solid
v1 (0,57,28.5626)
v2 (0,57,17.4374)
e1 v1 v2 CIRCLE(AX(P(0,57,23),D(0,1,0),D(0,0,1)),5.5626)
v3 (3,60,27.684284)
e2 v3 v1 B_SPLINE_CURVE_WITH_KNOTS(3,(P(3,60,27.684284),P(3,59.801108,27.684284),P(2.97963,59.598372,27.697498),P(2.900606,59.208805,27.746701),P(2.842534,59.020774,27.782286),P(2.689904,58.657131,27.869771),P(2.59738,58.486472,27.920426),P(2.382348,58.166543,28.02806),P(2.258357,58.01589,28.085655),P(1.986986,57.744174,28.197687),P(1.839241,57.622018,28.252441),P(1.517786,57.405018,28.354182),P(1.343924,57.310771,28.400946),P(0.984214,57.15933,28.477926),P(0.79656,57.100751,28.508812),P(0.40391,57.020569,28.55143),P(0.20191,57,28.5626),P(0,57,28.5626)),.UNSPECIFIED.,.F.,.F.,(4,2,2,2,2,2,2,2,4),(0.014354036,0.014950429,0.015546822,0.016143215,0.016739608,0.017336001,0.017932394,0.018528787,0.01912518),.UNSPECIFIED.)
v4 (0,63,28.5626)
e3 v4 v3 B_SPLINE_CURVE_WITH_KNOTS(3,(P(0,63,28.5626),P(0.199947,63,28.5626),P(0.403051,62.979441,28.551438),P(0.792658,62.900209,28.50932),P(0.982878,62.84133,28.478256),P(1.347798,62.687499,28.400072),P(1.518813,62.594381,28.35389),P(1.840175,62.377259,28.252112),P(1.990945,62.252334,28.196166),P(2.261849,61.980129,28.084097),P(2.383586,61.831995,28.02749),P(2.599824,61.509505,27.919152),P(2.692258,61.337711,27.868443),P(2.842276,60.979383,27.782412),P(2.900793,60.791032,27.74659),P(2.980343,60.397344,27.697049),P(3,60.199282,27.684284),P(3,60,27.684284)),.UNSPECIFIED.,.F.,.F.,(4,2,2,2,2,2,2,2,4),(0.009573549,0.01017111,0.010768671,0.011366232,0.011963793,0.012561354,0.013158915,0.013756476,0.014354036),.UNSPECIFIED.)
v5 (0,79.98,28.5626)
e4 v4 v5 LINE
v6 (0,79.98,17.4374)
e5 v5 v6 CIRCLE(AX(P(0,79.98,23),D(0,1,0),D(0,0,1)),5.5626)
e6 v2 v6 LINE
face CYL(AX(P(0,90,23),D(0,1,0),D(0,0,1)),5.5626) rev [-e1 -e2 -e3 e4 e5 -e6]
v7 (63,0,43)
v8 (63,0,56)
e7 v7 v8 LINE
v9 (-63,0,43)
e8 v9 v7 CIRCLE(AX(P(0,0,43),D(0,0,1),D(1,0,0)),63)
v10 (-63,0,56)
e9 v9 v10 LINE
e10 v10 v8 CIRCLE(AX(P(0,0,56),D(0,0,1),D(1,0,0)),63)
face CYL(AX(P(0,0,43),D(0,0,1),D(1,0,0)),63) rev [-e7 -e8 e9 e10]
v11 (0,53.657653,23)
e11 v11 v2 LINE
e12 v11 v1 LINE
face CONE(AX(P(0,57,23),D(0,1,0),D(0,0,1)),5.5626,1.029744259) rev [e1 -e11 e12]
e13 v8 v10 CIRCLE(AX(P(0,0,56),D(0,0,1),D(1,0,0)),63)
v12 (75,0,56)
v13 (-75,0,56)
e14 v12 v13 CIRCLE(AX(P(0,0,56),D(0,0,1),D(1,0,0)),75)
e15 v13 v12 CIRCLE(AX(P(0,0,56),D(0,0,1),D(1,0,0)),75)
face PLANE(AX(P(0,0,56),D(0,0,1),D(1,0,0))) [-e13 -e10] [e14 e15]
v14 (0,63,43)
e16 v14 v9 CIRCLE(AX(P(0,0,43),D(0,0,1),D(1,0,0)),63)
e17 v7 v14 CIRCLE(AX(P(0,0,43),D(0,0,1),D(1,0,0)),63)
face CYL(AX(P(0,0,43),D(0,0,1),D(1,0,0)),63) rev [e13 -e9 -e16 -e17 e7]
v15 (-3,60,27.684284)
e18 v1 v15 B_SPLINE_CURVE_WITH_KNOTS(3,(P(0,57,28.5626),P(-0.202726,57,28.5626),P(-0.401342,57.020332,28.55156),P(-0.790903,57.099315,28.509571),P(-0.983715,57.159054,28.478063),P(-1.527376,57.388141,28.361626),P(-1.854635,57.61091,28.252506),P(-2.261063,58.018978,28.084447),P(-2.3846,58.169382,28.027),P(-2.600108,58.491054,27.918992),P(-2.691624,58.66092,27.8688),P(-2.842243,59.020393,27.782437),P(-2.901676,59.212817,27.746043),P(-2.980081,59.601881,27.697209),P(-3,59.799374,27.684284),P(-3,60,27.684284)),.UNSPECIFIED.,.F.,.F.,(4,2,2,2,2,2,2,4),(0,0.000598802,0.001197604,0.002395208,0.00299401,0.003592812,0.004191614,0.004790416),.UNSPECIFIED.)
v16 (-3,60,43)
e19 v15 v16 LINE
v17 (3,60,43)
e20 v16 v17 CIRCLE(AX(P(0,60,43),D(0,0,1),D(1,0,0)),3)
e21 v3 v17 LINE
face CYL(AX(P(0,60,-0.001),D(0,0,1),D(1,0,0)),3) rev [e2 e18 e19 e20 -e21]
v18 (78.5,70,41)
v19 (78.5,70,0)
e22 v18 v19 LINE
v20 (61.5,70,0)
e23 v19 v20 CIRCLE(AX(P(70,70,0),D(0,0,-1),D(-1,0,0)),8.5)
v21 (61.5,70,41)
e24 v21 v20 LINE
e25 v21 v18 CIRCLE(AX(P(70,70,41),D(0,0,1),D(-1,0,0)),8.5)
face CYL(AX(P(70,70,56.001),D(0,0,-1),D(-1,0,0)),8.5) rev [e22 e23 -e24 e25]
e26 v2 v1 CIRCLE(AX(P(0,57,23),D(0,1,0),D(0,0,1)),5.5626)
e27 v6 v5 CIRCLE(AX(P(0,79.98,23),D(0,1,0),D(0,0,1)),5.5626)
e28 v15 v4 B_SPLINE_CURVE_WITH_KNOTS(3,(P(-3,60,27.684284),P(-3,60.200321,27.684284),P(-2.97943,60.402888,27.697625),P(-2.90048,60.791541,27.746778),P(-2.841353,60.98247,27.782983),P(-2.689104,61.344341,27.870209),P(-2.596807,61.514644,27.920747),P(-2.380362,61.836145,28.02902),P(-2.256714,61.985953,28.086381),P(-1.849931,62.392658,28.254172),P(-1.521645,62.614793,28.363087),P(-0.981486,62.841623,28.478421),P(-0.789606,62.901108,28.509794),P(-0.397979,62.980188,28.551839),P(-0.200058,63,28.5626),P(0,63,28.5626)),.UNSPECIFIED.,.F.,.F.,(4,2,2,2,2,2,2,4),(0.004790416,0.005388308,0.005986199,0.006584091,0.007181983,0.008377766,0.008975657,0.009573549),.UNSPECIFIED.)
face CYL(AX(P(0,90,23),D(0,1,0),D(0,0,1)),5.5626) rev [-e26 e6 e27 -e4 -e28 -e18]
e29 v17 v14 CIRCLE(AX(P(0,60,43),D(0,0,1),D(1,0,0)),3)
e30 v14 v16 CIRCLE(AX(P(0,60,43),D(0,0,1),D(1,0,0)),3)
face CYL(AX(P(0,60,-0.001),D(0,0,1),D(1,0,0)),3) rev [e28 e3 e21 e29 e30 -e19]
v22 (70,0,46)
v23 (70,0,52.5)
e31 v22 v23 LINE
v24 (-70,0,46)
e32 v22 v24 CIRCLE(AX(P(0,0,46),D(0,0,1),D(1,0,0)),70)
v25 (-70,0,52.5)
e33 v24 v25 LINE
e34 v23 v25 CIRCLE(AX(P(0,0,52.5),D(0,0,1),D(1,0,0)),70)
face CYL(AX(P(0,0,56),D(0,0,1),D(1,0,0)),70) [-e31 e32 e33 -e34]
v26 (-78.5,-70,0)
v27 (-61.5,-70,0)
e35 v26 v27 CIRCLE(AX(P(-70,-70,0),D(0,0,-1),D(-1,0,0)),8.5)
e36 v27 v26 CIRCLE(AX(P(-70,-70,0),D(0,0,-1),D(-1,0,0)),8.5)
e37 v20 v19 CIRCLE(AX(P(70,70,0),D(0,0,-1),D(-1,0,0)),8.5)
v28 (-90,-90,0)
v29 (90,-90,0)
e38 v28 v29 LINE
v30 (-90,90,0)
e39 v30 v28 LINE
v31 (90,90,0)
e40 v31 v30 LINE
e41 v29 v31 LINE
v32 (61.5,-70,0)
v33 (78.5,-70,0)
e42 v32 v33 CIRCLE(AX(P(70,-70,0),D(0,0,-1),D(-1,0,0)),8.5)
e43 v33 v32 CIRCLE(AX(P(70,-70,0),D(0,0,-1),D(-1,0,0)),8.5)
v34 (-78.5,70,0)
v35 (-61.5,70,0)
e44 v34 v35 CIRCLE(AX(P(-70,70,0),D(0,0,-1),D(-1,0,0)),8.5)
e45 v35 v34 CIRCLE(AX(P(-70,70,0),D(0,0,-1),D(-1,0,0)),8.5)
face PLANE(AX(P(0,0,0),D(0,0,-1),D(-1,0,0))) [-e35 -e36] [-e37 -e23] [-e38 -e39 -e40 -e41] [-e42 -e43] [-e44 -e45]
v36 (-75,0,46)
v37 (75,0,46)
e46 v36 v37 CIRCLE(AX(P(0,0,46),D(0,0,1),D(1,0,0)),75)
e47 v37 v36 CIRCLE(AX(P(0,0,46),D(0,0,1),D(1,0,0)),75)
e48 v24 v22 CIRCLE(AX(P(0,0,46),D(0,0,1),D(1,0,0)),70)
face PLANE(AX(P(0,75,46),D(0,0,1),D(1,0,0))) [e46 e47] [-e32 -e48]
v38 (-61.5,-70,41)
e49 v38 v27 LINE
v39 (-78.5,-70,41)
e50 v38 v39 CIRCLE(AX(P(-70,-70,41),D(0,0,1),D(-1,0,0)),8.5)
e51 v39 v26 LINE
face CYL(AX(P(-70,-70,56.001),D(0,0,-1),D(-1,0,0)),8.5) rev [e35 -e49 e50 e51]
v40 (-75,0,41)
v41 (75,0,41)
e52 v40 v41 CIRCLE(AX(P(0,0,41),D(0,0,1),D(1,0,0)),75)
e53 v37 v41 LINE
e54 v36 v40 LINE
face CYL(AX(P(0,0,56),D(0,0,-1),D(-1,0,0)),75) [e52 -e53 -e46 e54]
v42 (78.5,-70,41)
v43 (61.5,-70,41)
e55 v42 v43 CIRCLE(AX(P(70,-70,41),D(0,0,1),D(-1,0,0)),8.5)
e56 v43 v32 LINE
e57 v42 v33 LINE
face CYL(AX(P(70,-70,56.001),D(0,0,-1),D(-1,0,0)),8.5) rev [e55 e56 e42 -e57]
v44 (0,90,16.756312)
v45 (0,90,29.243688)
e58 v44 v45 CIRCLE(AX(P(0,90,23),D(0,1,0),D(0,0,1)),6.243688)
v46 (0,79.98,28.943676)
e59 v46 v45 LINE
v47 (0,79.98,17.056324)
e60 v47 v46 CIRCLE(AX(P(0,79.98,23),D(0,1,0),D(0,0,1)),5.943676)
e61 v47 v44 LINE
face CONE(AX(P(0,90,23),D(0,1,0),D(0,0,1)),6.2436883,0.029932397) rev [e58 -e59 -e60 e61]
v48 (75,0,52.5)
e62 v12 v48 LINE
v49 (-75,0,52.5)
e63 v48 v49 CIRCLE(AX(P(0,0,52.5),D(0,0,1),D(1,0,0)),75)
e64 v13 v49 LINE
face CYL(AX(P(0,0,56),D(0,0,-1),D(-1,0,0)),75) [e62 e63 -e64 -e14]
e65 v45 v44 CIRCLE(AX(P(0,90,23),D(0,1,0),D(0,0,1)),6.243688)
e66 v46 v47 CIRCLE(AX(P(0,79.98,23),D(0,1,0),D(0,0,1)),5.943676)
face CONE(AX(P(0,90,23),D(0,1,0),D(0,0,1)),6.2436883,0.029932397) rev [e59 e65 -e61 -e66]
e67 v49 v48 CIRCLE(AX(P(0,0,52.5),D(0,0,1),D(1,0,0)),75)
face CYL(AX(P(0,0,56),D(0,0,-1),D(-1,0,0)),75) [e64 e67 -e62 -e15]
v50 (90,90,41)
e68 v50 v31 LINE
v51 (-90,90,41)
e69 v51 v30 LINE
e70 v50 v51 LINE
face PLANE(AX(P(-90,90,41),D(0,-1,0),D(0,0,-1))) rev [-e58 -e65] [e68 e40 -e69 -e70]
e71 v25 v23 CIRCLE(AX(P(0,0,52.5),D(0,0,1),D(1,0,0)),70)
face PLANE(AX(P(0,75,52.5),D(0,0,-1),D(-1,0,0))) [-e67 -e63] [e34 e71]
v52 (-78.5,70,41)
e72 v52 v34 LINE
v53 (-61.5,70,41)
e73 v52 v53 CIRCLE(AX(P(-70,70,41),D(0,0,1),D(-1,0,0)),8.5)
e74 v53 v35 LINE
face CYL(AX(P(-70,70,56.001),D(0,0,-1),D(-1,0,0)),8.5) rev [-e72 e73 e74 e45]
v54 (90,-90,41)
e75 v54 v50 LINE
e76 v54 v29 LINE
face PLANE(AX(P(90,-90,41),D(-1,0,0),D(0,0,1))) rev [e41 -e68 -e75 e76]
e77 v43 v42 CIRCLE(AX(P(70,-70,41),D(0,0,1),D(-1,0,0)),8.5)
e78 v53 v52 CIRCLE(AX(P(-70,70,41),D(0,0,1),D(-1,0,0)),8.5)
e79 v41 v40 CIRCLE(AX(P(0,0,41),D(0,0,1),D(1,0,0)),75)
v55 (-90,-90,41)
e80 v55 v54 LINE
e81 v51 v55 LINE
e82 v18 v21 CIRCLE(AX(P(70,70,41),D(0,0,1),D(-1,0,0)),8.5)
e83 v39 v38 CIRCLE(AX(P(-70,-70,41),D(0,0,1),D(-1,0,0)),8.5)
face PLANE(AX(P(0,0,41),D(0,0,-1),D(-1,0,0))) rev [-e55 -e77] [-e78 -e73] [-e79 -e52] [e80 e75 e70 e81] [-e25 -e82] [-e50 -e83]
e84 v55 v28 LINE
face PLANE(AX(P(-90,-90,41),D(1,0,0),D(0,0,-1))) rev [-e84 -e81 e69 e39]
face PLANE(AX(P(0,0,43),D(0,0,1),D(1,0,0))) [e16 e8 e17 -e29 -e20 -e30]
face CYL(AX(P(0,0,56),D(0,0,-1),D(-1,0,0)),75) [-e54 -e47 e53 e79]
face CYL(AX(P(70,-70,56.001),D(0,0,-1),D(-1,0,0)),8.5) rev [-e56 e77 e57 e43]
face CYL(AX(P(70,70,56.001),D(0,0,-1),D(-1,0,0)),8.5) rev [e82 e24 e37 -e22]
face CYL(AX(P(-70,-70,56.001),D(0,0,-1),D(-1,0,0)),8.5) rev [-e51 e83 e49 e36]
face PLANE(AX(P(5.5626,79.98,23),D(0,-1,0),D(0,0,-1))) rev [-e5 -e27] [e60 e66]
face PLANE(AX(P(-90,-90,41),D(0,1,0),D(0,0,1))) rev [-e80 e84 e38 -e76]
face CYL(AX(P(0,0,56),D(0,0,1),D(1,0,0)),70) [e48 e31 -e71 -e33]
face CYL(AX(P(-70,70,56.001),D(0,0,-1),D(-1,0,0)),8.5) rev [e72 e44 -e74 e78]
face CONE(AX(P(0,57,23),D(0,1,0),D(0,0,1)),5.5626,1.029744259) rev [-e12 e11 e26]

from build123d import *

# Parameters (mm, degrees)
SKETCH_1_W               = 180
SKETCH_1_H               = 180
EXTRUDE_1_DEPTH          = 41
SKETCH_2_R               = 75
EXTRUDE_2_DEPTH          = 15
SKETCH_3_R               = 63
CUT_EXTRUDE_1_DEPTH      = 13
SKETCH_4_W               = 6.5
SKETCH_4_H               = 5
CUT_EXTRUDE_2_REACH      = 136.347
CUT_EXTRUDE_2_END_RADIUS = 5.5626
SKETCH_9_R               = 3
CUT_EXTRUDE_4_REACH      = 141.054
SKETCH_11_R              = 8.5


with BuildPart() as part:
    # 草图1 → 凸台-拉伸1 (new body)
    with BuildSketch(Plane.XY):
        Rectangle(SKETCH_1_W, SKETCH_1_H)
    extrude(amount=EXTRUDE_1_DEPTH)

    # 草图2 → 凸台-拉伸2 (add)
    with BuildSketch(Plane.XY.offset(41)):
        Circle(SKETCH_2_R)
    extrude(amount=EXTRUDE_2_DEPTH)

    # 草图3 → 切除-拉伸1 (cut)
    with BuildSketch(Plane.XY.offset(56)):
        Circle(SKETCH_3_R)
    extrude(amount=-CUT_EXTRUDE_1_DEPTH, mode=Mode.SUBTRACT)

    # 草图4 → 切除-旋转1 (revolve, cut)
    with BuildSketch(Plane(origin=(0, 0, 0), x_dir=(0, 0, -1), z_dir=(1, 0, 0)), mode=Mode.PRIVATE) as cut_revolve_1_sk:
        with Locations((-49.25, 72.5)):
            Rectangle(SKETCH_4_W, SKETCH_4_H)
    revolve(cut_revolve_1_sk.sketch.rotate(Axis((0, 0, 56), (0, 0, -1)), 90), axis=Axis((0, 0, 56), (0, 0, -1)), mode=Mode.SUBTRACT)

    # 草图6 → 1/4 NPT 螺纹孔1 (revolve, cut)
    with BuildSketch(Plane(origin=(0, 90, 23), x_dir=(0, 0, 1), z_dir=(1, 0, 0))):
        Polygon((0, 0), (0, 36.342347279), (5.5626, 33), (5.5626, 10.02), (5.943676082, 10.02), (6.2436883, 0), align=None)
    revolve(axis=Axis((0, 96.35, 23), (0, -1, 0)), mode=Mode.SUBTRACT)

    # 切除-拉伸2: up to this cylinder (the profile starts outside it)
    cut_extrude_2_end = Plane(origin=(0, 60, 23), z_dir=(0, 1, 0)) * Cylinder(CUT_EXTRUDE_2_END_RADIUS, 284.8192, mode=Mode.PRIVATE)
    # 草图9 → 切除-拉伸2 (cut, up to the surface)
    with BuildSketch(Plane.XY.offset(43), mode=Mode.PRIVATE) as cut_extrude_2_sk1:
        with Locations(Location((0, 60, 0), (0, 0, 270))):
            Circle(SKETCH_9_R)
    cut_extrude_2_tool1 = extrude(cut_extrude_2_sk1.sketch, amount=-CUT_EXTRUDE_2_REACH, mode=Mode.PRIVATE) - cut_extrude_2_end
    add(cut_extrude_2_tool1.solids().sort_by_distance((0, 60, 43))[0], mode=Mode.SUBTRACT)

    # 草图11 → 切除-拉伸4 (cut, up to next)
    with BuildSketch(Plane(origin=(0, 0, 0), x_dir=(-1, 0, 0), z_dir=(0, 0, -1)), mode=Mode.PRIVATE) as cut_extrude_4_sk1:
        with Locations((-70, 70)):
            Circle(SKETCH_11_R)
    cut_extrude_4_tool1 = extrude(cut_extrude_4_sk1.sketch, amount=-CUT_EXTRUDE_4_REACH, mode=Mode.PRIVATE) & part.part
    # 草图11 → 切除-拉伸4 (cut, up to next)
    with BuildSketch(Plane(origin=(0, 0, 0), x_dir=(-1, 0, 0), z_dir=(0, 0, -1)), mode=Mode.PRIVATE) as cut_extrude_4_sk2:
        with Locations((70, 70)):
            Circle(SKETCH_11_R)
    cut_extrude_4_tool2 = extrude(cut_extrude_4_sk2.sketch, amount=-CUT_EXTRUDE_4_REACH, mode=Mode.PRIVATE) & part.part
    # 草图11 → 切除-拉伸4 (cut, up to next)
    with BuildSketch(Plane(origin=(0, 0, 0), x_dir=(-1, 0, 0), z_dir=(0, 0, -1)), mode=Mode.PRIVATE) as cut_extrude_4_sk3:
        with Locations((70, -70)):
            Circle(SKETCH_11_R)
    cut_extrude_4_tool3 = extrude(cut_extrude_4_sk3.sketch, amount=-CUT_EXTRUDE_4_REACH, mode=Mode.PRIVATE) & part.part
    # 草图11 → 切除-拉伸4 (cut, up to next)
    with BuildSketch(Plane(origin=(0, 0, 0), x_dir=(-1, 0, 0), z_dir=(0, 0, -1)), mode=Mode.PRIVATE) as cut_extrude_4_sk4:
        with Locations((-70, -70)):
            Circle(SKETCH_11_R)
    cut_extrude_4_tool4 = extrude(cut_extrude_4_sk4.sketch, amount=-CUT_EXTRUDE_4_REACH, mode=Mode.PRIVATE) & part.part
    add(cut_extrude_4_tool1.solids().sort_by_distance((70, 70, 0))[0], mode=Mode.SUBTRACT)
    add(cut_extrude_4_tool2.solids().sort_by_distance((-70, 70, 0))[0], mode=Mode.SUBTRACT)
    add(cut_extrude_4_tool3.solids().sort_by_distance((-70, -70, 0))[0], mode=Mode.SUBTRACT)
    add(cut_extrude_4_tool4.solids().sort_by_distance((70, -70, 0))[0], mode=Mode.SUBTRACT)


solid = part.part
